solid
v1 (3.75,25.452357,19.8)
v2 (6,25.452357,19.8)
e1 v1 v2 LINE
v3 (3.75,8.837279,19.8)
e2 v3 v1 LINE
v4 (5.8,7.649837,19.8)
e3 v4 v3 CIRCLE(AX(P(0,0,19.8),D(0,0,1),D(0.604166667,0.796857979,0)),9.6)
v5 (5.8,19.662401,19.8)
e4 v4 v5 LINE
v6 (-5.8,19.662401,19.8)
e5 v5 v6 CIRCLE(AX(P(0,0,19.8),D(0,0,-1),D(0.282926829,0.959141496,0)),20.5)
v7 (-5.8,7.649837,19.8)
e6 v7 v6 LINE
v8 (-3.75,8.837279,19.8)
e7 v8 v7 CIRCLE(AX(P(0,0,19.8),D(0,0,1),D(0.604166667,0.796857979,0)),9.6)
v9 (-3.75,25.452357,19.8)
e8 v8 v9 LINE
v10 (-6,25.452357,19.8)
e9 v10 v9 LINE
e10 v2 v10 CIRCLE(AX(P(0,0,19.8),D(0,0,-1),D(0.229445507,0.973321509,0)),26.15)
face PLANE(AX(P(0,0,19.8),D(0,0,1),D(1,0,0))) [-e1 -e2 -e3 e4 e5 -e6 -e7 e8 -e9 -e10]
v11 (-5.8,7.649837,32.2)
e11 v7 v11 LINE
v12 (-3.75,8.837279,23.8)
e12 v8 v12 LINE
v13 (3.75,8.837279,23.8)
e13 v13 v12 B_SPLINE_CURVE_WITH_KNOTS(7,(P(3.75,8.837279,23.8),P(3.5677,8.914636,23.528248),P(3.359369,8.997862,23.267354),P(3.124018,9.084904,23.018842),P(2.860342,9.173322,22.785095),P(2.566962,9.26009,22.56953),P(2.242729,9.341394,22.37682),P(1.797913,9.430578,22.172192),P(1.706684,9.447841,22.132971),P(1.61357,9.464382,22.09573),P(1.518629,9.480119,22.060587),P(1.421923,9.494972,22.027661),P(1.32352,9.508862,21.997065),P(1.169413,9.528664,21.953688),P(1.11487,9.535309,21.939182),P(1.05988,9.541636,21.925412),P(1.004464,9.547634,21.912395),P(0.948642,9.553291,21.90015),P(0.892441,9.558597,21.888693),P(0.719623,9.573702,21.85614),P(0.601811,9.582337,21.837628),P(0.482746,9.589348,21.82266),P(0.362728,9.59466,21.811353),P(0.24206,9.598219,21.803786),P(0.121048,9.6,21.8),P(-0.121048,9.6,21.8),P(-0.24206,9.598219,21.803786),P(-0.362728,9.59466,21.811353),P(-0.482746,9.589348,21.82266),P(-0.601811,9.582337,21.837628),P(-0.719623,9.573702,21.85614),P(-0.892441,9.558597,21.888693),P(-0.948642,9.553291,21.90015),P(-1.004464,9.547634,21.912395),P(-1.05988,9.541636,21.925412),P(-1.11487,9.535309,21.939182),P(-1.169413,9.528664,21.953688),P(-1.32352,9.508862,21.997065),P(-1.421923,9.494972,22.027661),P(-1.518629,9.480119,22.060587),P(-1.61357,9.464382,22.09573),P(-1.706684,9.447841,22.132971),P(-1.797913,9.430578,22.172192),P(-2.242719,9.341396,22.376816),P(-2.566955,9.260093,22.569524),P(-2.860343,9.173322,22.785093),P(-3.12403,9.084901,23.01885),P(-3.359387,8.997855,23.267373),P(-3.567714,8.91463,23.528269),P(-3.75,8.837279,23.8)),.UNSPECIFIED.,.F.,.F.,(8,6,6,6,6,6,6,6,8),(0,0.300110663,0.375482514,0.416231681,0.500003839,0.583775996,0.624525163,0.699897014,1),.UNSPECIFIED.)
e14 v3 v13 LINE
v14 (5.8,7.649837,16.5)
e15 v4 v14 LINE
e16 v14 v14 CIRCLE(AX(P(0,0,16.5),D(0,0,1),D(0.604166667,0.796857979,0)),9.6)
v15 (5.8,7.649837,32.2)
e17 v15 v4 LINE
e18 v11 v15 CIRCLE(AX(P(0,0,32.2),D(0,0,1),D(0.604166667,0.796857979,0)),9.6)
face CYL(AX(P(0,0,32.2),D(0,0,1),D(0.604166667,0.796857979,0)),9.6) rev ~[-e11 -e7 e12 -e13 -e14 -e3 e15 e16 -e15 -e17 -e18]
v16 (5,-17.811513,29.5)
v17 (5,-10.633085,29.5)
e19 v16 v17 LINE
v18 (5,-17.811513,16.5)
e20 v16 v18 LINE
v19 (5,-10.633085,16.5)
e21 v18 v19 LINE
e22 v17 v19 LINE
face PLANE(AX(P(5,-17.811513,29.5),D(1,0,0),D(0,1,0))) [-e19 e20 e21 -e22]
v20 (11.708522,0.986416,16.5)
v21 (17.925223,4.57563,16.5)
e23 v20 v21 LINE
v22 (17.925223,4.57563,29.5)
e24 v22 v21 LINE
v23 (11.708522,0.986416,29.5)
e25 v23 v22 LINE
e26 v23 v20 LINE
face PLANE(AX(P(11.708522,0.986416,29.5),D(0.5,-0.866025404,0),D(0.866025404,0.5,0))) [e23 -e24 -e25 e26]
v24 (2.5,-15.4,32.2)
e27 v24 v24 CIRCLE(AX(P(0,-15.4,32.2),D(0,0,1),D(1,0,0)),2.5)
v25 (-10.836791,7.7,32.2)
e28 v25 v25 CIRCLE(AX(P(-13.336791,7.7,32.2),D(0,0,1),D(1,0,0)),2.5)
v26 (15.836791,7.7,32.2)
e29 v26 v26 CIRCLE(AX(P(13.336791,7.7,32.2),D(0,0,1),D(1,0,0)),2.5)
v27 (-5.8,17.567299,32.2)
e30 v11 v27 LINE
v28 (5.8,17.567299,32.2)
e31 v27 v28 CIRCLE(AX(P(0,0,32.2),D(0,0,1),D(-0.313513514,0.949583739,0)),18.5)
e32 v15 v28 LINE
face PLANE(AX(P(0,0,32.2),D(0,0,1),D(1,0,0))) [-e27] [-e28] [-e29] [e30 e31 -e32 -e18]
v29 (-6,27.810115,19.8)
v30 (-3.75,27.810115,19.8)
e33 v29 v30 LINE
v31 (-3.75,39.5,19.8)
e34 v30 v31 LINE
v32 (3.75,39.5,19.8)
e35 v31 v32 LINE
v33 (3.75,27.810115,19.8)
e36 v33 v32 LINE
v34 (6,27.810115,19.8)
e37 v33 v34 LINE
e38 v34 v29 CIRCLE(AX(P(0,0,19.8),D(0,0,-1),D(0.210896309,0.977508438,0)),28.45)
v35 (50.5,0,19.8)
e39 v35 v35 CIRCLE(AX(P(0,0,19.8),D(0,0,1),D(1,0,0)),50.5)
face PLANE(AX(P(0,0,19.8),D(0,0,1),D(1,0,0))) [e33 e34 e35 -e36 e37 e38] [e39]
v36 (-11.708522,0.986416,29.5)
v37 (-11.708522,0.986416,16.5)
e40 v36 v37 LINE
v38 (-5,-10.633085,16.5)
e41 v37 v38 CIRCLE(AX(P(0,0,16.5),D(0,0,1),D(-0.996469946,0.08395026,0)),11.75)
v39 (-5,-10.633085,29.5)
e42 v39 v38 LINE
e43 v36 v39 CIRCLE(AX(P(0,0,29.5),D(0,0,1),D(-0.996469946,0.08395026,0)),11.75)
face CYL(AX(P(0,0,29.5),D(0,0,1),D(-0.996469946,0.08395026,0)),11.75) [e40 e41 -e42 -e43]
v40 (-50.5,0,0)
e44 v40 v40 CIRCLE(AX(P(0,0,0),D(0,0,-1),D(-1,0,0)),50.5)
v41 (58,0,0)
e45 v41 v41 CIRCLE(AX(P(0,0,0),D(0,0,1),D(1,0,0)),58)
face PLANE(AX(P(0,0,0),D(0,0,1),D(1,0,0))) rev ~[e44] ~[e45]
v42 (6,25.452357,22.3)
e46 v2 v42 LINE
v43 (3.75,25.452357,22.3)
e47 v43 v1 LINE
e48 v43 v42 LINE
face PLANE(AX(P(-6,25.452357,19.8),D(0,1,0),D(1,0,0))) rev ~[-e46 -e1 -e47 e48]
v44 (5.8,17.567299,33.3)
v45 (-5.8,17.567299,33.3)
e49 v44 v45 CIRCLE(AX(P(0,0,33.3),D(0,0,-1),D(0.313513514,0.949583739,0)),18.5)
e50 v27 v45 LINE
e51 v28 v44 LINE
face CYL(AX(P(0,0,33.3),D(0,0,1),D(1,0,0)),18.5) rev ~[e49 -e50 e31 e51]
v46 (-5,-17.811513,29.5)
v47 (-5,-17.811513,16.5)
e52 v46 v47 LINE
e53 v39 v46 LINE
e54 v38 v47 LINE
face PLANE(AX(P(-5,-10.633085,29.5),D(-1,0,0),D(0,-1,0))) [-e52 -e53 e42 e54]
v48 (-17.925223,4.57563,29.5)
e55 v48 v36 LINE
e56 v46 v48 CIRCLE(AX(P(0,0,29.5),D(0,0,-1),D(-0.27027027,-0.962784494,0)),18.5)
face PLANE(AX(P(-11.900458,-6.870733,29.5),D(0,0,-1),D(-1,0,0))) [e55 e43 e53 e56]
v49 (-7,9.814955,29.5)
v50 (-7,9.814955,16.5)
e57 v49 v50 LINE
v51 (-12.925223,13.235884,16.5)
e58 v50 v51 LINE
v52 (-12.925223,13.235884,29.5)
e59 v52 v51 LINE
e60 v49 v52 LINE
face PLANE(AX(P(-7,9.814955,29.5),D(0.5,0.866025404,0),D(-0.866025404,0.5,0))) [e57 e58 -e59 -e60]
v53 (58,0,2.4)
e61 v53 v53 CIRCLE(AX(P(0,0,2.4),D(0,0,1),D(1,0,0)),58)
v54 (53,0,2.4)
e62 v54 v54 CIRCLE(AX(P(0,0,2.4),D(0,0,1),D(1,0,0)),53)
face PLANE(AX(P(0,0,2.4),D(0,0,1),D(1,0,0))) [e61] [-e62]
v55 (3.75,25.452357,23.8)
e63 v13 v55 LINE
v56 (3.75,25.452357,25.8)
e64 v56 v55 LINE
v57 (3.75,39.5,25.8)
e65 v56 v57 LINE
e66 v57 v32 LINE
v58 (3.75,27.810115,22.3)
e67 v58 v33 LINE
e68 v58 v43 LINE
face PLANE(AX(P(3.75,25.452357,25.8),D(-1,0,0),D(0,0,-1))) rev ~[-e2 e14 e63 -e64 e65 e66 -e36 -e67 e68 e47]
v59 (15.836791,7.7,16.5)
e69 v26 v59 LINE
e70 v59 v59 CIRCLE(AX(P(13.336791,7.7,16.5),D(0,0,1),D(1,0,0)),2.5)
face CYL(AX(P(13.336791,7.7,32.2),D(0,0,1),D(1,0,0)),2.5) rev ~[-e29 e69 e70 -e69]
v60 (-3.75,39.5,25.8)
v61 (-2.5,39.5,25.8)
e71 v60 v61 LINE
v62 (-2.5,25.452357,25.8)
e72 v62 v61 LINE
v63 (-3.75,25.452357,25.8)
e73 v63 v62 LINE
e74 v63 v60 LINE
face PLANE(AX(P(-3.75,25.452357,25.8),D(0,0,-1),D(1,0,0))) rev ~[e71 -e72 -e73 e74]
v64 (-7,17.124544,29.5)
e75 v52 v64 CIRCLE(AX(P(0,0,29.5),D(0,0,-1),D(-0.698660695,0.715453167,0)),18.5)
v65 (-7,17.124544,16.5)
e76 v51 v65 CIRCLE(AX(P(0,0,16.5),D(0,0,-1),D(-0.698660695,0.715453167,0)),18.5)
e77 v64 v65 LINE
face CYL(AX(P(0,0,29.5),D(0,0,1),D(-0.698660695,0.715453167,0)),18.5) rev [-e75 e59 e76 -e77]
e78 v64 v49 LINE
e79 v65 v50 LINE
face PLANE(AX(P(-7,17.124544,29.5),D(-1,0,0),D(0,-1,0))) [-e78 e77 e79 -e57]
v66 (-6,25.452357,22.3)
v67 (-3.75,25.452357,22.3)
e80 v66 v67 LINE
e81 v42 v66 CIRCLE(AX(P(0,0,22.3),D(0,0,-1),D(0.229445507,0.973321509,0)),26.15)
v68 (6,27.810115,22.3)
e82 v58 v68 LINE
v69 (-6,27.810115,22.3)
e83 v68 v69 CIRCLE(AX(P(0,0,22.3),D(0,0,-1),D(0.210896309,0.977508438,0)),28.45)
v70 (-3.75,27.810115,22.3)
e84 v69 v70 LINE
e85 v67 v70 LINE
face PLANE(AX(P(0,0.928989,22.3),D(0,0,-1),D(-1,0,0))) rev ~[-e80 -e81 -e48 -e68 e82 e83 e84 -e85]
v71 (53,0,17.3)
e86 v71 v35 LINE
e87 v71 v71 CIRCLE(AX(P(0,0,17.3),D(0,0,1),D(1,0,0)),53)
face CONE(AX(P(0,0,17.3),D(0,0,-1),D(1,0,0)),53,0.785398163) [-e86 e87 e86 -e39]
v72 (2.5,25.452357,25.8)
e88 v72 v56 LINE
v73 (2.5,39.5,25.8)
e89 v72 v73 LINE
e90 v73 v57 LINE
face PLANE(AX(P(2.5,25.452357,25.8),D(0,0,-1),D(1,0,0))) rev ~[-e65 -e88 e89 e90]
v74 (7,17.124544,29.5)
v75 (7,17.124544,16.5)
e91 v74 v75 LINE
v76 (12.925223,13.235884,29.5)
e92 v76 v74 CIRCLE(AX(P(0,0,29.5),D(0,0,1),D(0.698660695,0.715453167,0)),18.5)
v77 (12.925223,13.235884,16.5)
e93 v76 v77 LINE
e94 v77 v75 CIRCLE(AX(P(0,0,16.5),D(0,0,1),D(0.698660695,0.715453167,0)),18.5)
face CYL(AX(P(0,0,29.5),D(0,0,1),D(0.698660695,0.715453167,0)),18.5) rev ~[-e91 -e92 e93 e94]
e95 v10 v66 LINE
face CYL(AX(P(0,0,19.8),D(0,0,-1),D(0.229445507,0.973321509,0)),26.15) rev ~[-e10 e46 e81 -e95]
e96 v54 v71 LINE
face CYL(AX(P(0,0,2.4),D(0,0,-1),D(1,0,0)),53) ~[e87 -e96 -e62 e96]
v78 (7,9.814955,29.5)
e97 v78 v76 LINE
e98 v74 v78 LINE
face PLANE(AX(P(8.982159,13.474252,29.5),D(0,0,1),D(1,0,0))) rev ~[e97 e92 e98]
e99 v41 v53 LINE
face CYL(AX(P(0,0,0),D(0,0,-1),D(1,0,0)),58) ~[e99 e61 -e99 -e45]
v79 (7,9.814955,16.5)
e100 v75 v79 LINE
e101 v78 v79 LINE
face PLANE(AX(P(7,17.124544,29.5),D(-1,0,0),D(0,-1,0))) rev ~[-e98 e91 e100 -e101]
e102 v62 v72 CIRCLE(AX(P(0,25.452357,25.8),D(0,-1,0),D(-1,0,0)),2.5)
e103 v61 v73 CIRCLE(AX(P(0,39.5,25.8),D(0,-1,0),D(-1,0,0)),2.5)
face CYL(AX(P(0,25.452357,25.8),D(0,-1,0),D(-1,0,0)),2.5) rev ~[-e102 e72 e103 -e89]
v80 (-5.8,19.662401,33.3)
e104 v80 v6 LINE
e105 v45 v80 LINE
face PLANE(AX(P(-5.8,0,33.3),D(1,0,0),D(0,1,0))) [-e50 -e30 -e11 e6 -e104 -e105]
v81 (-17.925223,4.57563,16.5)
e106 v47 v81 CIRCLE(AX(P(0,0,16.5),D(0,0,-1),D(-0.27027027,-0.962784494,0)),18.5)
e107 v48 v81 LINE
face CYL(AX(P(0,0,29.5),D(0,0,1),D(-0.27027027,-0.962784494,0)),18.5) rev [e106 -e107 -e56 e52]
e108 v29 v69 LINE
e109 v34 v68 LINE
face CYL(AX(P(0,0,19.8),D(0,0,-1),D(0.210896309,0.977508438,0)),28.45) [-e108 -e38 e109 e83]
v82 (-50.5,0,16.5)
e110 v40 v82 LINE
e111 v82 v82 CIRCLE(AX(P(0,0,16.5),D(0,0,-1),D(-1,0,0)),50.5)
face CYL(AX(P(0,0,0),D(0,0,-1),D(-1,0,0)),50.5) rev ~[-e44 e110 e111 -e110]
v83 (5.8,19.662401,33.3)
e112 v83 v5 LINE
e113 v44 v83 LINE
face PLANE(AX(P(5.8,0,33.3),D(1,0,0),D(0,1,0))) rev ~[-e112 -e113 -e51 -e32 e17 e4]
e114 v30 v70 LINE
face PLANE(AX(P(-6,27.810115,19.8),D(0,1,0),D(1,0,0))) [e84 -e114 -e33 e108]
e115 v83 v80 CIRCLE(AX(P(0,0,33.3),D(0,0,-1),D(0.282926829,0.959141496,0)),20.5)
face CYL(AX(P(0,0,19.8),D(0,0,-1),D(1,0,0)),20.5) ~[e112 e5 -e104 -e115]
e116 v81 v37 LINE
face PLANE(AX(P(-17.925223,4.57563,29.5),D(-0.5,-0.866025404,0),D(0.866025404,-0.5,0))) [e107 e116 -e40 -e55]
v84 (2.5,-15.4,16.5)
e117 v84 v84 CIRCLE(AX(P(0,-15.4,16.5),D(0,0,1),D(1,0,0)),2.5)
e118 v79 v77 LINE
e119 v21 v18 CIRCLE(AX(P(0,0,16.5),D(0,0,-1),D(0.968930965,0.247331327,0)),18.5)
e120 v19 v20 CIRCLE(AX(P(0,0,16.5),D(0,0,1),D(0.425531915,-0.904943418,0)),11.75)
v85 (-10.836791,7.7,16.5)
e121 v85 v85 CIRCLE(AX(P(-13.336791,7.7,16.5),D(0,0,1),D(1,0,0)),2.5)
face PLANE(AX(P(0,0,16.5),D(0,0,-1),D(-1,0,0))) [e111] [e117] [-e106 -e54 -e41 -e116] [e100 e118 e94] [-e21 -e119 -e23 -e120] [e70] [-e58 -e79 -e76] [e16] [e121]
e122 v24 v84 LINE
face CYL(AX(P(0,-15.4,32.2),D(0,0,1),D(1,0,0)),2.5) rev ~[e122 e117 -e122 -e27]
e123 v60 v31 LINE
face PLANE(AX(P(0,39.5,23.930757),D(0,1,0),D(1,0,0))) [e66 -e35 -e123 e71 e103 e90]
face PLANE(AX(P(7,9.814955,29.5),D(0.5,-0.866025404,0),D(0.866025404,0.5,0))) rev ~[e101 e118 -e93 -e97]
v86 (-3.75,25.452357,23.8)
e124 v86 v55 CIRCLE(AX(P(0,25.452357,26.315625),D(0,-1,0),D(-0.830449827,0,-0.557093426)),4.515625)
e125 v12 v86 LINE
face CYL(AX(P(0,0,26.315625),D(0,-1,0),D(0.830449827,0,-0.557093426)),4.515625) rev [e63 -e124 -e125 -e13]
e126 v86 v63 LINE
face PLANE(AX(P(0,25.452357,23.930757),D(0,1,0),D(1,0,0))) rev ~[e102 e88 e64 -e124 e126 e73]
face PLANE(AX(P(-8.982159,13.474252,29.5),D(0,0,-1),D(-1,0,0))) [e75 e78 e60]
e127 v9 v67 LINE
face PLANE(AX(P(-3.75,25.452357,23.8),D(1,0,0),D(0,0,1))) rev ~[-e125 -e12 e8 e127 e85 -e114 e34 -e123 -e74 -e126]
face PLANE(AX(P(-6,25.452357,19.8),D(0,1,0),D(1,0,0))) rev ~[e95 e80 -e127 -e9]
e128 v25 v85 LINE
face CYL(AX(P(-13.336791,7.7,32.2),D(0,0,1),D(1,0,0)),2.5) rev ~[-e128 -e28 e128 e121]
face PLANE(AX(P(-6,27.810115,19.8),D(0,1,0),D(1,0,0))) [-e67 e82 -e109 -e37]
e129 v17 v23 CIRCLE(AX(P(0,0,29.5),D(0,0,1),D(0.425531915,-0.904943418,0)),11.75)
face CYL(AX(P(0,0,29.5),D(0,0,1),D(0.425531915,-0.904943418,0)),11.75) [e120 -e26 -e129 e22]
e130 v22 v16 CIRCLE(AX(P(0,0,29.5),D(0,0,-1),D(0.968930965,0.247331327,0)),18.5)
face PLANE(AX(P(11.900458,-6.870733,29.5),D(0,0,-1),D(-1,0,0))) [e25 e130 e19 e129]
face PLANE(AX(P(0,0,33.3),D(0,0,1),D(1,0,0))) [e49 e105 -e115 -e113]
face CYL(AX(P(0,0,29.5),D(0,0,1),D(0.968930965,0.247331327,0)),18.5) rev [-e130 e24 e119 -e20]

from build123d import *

# Parameters (mm, degrees)
SKETCH_1_R          = 58
EXTRUDE_1_DEPTH     = 2.4
SKETCH_2_R          = 53
EXTRUDE_2_DEPTH     = 17.4
CHAMFER_1_SIZE      = 2.5
SKETCH_3_R          = 20.5
EXTRUDE_3_DEPTH     = 13.5
SKETCH_4_R          = 18.5
CUT_EXTRUDE_1_DEPTH = 1.1
SKETCH_5_R          = 2.5
CUT_EXTRUDE_2_DEPTH = 320
SKETCH_6_R          = 50.5
CUT_EXTRUDE_3_DEPTH = 16.5
CUT_EXTRUDE_START   = -13
CUT_EXTRUDE_5_DEPTH = 13
EXTRUDE_4_DEPTH     = 2.5
SKETCH_9_W          = 11.6
SKETCH_9_H          = 21.886068862
CUT_EXTRUDE_6_DEPTH = 13.5
EXTRUDE_5_DEPTH     = 39.5
EXTRUDE_START       = -14.047642545
EXTRUDE_6_DEPTH     = 14.047642545
CUT_EXTRUDE_7_REACH = 90.118
SKETCH_10_R         = 9.6


with BuildPart() as part:
    # 草图1 → 凸台-拉伸1 (new body)
    with BuildSketch(Plane.XY):
        Circle(SKETCH_1_R)
    extrude(amount=EXTRUDE_1_DEPTH)

    # 草图2 → 凸台-拉伸2 (add)
    with BuildSketch(Plane.XY.offset(2.4)):
        Circle(SKETCH_2_R)
    extrude(amount=EXTRUDE_2_DEPTH)

    # 倒角1
    chamfer_1_edges = [part.edges().sort_by_distance(p)[0] for p in [
        (-53, 0, 19.8),
    ]]
    chamfer(chamfer_1_edges, length=CHAMFER_1_SIZE)

    # 草图3 → 凸台-拉伸3 (add)
    with BuildSketch(Plane.XY.offset(19.8)):
        Circle(SKETCH_3_R)
    extrude(amount=EXTRUDE_3_DEPTH)

    # 草图4 → 切除-拉伸1 (cut)
    with BuildSketch(Plane.XY.offset(33.3)):
        Circle(SKETCH_4_R)
    extrude(amount=-CUT_EXTRUDE_1_DEPTH, mode=Mode.SUBTRACT)

    # 草图5 → 切除-拉伸2 (cut)
    with BuildSketch(Plane.XY.offset(32.2)):
        with Locations((0, -15.4)):
            Circle(SKETCH_5_R)
        with Locations((-13.336791218, 7.7)):
            Circle(SKETCH_5_R)
        with Locations((13.336791218, 7.7)):
            Circle(SKETCH_5_R)
    extrude(amount=-CUT_EXTRUDE_2_DEPTH, mode=Mode.SUBTRACT)

    # 草图6 → 切除-拉伸3 (cut)
    with BuildSketch(Plane(origin=(0, 0, 0), x_dir=(-1, 0, 0), z_dir=(0, 0, -1))):
        Circle(SKETCH_6_R)
    extrude(amount=-CUT_EXTRUDE_3_DEPTH, mode=Mode.SUBTRACT)

    # 草图7 → 切除-拉伸5 (cut)
    with BuildSketch(Plane(origin=(0, 0, 16.5), x_dir=(-1, 0, 0), z_dir=(0, 0, -1)).offset(CUT_EXTRUDE_START)):
        with BuildLine():
            Line((-11.708521868, 0.986415561), (-17.925222851, 4.575629546))
            ThreePointArc((-17.925222851, 4.575629546), (-16.02146997, -9.25), (-5, -17.811513131))
            Line((-5, -17.811513131), (-5, -10.633085159))
            ThreePointArc((-5, -10.633085159), (-10.175798494, -5.875), (-11.708521868, 0.986415561))
        make_face()
        with BuildLine():
            Line((5, -10.633085159), (5, -17.811513131))
            ThreePointArc((5, -17.811513131), (16.02146997, -9.25), (17.925222851, 4.575629546))
            Line((17.925222851, 4.575629546), (11.708521868, 0.986415561))
            ThreePointArc((11.708521868, 0.986415561), (10.175798494, -5.875), (5, -10.633085159))
        make_face()
        with BuildLine():
            Line((-7, 9.814954576), (-12.925222851, 13.235883584))
            ThreePointArc((-12.925222851, 13.235883584), (-10.150568751, 15.466607709), (-7, 17.12454379))
            Line((-7, 17.12454379), (-7, 9.814954576))
        make_face()
        with BuildLine():
            Line((7, 9.814954576), (12.925222851, 13.235883584))
            ThreePointArc((12.925222851, 13.235883584), (10.150568751, 15.466607709), (7, 17.12454379))
            Line((7, 17.12454379), (7, 9.814954576))
        make_face()
    extrude(amount=CUT_EXTRUDE_5_DEPTH, mode=Mode.SUBTRACT)

    # 草图8 → 凸台-拉伸4 (add)
    with BuildSketch(Plane.XY.offset(19.8)):
        with BuildLine():
            Line((-6, 27.810115066), (6, 27.810115066))
            ThreePointArc((6, 27.810115066), (0, -28.45), (-6, 27.810115066))
        make_face()
        with BuildLine():
            Line((-6, 25.452357455), (6, 25.452357455))
            ThreePointArc((6, 25.452357455), (0, -26.15), (-6, 25.452357455))
        make_face(mode=Mode.SUBTRACT)
    extrude(amount=EXTRUDE_4_DEPTH)

    # 草图9 → 切除-拉伸6 (cut)
    with BuildSketch(Plane.XY.offset(33.3)):
        with Locations((0, 10.943034431)):
            Rectangle(SKETCH_9_W, SKETCH_9_H)
    extrude(amount=-CUT_EXTRUDE_6_DEPTH, mode=Mode.SUBTRACT)

    # 草图11 → 凸台-拉伸5 (add)
    with BuildSketch(Plane(origin=(0, 0, 0), x_dir=(1, 0, 0), z_dir=(0, 1, 0))):
        with BuildLine():
            Line((-3.75, -19.8), (3.75, -19.8))
            Line((3.75, -19.8), (3.75, -23.8))
            ThreePointArc((3.75, -23.8), (0, -21.8), (-3.75, -23.8))
            Line((-3.75, -23.8), (-3.75, -19.8))
        make_face()
    extrude(amount=EXTRUDE_5_DEPTH)

    # 草图12 → 凸台-拉伸6 (add)
    with BuildSketch(Plane(origin=(0, 39.5, 0), x_dir=(1, 0, 0), z_dir=(0, 1, 0)).offset(EXTRUDE_START)):
        with BuildLine():
            Line((-3.75, -23.8), (-3.75, -25.8))
            Line((-3.75, -25.8), (-2.5, -25.8))
            ThreePointArc((-2.5, -25.8), (0, -23.3), (2.5, -25.8))
            Line((2.5, -25.8), (3.75, -25.8))
            Line((3.75, -25.8), (3.75, -23.8))
            ThreePointArc((3.75, -23.8), (0, -21.8), (-3.75, -23.8))
        make_face()
    extrude(amount=EXTRUDE_6_DEPTH)

    # 草图10 → 切除-拉伸7 (cut, up to next)
    with BuildSketch(Plane.XY.offset(32.2), mode=Mode.PRIVATE) as cut_extrude_7_sk1:
        with Locations(Location((0, 0, 0), (0, 0, 52.831100344))):
            Circle(SKETCH_10_R)
    cut_extrude_7_tool1 = extrude(cut_extrude_7_sk1.sketch, amount=-CUT_EXTRUDE_7_REACH, mode=Mode.PRIVATE) & part.part
    add(cut_extrude_7_tool1.solids().sort_by_distance((0, 0, 32.2))[0], mode=Mode.SUBTRACT)


solid = part.part
